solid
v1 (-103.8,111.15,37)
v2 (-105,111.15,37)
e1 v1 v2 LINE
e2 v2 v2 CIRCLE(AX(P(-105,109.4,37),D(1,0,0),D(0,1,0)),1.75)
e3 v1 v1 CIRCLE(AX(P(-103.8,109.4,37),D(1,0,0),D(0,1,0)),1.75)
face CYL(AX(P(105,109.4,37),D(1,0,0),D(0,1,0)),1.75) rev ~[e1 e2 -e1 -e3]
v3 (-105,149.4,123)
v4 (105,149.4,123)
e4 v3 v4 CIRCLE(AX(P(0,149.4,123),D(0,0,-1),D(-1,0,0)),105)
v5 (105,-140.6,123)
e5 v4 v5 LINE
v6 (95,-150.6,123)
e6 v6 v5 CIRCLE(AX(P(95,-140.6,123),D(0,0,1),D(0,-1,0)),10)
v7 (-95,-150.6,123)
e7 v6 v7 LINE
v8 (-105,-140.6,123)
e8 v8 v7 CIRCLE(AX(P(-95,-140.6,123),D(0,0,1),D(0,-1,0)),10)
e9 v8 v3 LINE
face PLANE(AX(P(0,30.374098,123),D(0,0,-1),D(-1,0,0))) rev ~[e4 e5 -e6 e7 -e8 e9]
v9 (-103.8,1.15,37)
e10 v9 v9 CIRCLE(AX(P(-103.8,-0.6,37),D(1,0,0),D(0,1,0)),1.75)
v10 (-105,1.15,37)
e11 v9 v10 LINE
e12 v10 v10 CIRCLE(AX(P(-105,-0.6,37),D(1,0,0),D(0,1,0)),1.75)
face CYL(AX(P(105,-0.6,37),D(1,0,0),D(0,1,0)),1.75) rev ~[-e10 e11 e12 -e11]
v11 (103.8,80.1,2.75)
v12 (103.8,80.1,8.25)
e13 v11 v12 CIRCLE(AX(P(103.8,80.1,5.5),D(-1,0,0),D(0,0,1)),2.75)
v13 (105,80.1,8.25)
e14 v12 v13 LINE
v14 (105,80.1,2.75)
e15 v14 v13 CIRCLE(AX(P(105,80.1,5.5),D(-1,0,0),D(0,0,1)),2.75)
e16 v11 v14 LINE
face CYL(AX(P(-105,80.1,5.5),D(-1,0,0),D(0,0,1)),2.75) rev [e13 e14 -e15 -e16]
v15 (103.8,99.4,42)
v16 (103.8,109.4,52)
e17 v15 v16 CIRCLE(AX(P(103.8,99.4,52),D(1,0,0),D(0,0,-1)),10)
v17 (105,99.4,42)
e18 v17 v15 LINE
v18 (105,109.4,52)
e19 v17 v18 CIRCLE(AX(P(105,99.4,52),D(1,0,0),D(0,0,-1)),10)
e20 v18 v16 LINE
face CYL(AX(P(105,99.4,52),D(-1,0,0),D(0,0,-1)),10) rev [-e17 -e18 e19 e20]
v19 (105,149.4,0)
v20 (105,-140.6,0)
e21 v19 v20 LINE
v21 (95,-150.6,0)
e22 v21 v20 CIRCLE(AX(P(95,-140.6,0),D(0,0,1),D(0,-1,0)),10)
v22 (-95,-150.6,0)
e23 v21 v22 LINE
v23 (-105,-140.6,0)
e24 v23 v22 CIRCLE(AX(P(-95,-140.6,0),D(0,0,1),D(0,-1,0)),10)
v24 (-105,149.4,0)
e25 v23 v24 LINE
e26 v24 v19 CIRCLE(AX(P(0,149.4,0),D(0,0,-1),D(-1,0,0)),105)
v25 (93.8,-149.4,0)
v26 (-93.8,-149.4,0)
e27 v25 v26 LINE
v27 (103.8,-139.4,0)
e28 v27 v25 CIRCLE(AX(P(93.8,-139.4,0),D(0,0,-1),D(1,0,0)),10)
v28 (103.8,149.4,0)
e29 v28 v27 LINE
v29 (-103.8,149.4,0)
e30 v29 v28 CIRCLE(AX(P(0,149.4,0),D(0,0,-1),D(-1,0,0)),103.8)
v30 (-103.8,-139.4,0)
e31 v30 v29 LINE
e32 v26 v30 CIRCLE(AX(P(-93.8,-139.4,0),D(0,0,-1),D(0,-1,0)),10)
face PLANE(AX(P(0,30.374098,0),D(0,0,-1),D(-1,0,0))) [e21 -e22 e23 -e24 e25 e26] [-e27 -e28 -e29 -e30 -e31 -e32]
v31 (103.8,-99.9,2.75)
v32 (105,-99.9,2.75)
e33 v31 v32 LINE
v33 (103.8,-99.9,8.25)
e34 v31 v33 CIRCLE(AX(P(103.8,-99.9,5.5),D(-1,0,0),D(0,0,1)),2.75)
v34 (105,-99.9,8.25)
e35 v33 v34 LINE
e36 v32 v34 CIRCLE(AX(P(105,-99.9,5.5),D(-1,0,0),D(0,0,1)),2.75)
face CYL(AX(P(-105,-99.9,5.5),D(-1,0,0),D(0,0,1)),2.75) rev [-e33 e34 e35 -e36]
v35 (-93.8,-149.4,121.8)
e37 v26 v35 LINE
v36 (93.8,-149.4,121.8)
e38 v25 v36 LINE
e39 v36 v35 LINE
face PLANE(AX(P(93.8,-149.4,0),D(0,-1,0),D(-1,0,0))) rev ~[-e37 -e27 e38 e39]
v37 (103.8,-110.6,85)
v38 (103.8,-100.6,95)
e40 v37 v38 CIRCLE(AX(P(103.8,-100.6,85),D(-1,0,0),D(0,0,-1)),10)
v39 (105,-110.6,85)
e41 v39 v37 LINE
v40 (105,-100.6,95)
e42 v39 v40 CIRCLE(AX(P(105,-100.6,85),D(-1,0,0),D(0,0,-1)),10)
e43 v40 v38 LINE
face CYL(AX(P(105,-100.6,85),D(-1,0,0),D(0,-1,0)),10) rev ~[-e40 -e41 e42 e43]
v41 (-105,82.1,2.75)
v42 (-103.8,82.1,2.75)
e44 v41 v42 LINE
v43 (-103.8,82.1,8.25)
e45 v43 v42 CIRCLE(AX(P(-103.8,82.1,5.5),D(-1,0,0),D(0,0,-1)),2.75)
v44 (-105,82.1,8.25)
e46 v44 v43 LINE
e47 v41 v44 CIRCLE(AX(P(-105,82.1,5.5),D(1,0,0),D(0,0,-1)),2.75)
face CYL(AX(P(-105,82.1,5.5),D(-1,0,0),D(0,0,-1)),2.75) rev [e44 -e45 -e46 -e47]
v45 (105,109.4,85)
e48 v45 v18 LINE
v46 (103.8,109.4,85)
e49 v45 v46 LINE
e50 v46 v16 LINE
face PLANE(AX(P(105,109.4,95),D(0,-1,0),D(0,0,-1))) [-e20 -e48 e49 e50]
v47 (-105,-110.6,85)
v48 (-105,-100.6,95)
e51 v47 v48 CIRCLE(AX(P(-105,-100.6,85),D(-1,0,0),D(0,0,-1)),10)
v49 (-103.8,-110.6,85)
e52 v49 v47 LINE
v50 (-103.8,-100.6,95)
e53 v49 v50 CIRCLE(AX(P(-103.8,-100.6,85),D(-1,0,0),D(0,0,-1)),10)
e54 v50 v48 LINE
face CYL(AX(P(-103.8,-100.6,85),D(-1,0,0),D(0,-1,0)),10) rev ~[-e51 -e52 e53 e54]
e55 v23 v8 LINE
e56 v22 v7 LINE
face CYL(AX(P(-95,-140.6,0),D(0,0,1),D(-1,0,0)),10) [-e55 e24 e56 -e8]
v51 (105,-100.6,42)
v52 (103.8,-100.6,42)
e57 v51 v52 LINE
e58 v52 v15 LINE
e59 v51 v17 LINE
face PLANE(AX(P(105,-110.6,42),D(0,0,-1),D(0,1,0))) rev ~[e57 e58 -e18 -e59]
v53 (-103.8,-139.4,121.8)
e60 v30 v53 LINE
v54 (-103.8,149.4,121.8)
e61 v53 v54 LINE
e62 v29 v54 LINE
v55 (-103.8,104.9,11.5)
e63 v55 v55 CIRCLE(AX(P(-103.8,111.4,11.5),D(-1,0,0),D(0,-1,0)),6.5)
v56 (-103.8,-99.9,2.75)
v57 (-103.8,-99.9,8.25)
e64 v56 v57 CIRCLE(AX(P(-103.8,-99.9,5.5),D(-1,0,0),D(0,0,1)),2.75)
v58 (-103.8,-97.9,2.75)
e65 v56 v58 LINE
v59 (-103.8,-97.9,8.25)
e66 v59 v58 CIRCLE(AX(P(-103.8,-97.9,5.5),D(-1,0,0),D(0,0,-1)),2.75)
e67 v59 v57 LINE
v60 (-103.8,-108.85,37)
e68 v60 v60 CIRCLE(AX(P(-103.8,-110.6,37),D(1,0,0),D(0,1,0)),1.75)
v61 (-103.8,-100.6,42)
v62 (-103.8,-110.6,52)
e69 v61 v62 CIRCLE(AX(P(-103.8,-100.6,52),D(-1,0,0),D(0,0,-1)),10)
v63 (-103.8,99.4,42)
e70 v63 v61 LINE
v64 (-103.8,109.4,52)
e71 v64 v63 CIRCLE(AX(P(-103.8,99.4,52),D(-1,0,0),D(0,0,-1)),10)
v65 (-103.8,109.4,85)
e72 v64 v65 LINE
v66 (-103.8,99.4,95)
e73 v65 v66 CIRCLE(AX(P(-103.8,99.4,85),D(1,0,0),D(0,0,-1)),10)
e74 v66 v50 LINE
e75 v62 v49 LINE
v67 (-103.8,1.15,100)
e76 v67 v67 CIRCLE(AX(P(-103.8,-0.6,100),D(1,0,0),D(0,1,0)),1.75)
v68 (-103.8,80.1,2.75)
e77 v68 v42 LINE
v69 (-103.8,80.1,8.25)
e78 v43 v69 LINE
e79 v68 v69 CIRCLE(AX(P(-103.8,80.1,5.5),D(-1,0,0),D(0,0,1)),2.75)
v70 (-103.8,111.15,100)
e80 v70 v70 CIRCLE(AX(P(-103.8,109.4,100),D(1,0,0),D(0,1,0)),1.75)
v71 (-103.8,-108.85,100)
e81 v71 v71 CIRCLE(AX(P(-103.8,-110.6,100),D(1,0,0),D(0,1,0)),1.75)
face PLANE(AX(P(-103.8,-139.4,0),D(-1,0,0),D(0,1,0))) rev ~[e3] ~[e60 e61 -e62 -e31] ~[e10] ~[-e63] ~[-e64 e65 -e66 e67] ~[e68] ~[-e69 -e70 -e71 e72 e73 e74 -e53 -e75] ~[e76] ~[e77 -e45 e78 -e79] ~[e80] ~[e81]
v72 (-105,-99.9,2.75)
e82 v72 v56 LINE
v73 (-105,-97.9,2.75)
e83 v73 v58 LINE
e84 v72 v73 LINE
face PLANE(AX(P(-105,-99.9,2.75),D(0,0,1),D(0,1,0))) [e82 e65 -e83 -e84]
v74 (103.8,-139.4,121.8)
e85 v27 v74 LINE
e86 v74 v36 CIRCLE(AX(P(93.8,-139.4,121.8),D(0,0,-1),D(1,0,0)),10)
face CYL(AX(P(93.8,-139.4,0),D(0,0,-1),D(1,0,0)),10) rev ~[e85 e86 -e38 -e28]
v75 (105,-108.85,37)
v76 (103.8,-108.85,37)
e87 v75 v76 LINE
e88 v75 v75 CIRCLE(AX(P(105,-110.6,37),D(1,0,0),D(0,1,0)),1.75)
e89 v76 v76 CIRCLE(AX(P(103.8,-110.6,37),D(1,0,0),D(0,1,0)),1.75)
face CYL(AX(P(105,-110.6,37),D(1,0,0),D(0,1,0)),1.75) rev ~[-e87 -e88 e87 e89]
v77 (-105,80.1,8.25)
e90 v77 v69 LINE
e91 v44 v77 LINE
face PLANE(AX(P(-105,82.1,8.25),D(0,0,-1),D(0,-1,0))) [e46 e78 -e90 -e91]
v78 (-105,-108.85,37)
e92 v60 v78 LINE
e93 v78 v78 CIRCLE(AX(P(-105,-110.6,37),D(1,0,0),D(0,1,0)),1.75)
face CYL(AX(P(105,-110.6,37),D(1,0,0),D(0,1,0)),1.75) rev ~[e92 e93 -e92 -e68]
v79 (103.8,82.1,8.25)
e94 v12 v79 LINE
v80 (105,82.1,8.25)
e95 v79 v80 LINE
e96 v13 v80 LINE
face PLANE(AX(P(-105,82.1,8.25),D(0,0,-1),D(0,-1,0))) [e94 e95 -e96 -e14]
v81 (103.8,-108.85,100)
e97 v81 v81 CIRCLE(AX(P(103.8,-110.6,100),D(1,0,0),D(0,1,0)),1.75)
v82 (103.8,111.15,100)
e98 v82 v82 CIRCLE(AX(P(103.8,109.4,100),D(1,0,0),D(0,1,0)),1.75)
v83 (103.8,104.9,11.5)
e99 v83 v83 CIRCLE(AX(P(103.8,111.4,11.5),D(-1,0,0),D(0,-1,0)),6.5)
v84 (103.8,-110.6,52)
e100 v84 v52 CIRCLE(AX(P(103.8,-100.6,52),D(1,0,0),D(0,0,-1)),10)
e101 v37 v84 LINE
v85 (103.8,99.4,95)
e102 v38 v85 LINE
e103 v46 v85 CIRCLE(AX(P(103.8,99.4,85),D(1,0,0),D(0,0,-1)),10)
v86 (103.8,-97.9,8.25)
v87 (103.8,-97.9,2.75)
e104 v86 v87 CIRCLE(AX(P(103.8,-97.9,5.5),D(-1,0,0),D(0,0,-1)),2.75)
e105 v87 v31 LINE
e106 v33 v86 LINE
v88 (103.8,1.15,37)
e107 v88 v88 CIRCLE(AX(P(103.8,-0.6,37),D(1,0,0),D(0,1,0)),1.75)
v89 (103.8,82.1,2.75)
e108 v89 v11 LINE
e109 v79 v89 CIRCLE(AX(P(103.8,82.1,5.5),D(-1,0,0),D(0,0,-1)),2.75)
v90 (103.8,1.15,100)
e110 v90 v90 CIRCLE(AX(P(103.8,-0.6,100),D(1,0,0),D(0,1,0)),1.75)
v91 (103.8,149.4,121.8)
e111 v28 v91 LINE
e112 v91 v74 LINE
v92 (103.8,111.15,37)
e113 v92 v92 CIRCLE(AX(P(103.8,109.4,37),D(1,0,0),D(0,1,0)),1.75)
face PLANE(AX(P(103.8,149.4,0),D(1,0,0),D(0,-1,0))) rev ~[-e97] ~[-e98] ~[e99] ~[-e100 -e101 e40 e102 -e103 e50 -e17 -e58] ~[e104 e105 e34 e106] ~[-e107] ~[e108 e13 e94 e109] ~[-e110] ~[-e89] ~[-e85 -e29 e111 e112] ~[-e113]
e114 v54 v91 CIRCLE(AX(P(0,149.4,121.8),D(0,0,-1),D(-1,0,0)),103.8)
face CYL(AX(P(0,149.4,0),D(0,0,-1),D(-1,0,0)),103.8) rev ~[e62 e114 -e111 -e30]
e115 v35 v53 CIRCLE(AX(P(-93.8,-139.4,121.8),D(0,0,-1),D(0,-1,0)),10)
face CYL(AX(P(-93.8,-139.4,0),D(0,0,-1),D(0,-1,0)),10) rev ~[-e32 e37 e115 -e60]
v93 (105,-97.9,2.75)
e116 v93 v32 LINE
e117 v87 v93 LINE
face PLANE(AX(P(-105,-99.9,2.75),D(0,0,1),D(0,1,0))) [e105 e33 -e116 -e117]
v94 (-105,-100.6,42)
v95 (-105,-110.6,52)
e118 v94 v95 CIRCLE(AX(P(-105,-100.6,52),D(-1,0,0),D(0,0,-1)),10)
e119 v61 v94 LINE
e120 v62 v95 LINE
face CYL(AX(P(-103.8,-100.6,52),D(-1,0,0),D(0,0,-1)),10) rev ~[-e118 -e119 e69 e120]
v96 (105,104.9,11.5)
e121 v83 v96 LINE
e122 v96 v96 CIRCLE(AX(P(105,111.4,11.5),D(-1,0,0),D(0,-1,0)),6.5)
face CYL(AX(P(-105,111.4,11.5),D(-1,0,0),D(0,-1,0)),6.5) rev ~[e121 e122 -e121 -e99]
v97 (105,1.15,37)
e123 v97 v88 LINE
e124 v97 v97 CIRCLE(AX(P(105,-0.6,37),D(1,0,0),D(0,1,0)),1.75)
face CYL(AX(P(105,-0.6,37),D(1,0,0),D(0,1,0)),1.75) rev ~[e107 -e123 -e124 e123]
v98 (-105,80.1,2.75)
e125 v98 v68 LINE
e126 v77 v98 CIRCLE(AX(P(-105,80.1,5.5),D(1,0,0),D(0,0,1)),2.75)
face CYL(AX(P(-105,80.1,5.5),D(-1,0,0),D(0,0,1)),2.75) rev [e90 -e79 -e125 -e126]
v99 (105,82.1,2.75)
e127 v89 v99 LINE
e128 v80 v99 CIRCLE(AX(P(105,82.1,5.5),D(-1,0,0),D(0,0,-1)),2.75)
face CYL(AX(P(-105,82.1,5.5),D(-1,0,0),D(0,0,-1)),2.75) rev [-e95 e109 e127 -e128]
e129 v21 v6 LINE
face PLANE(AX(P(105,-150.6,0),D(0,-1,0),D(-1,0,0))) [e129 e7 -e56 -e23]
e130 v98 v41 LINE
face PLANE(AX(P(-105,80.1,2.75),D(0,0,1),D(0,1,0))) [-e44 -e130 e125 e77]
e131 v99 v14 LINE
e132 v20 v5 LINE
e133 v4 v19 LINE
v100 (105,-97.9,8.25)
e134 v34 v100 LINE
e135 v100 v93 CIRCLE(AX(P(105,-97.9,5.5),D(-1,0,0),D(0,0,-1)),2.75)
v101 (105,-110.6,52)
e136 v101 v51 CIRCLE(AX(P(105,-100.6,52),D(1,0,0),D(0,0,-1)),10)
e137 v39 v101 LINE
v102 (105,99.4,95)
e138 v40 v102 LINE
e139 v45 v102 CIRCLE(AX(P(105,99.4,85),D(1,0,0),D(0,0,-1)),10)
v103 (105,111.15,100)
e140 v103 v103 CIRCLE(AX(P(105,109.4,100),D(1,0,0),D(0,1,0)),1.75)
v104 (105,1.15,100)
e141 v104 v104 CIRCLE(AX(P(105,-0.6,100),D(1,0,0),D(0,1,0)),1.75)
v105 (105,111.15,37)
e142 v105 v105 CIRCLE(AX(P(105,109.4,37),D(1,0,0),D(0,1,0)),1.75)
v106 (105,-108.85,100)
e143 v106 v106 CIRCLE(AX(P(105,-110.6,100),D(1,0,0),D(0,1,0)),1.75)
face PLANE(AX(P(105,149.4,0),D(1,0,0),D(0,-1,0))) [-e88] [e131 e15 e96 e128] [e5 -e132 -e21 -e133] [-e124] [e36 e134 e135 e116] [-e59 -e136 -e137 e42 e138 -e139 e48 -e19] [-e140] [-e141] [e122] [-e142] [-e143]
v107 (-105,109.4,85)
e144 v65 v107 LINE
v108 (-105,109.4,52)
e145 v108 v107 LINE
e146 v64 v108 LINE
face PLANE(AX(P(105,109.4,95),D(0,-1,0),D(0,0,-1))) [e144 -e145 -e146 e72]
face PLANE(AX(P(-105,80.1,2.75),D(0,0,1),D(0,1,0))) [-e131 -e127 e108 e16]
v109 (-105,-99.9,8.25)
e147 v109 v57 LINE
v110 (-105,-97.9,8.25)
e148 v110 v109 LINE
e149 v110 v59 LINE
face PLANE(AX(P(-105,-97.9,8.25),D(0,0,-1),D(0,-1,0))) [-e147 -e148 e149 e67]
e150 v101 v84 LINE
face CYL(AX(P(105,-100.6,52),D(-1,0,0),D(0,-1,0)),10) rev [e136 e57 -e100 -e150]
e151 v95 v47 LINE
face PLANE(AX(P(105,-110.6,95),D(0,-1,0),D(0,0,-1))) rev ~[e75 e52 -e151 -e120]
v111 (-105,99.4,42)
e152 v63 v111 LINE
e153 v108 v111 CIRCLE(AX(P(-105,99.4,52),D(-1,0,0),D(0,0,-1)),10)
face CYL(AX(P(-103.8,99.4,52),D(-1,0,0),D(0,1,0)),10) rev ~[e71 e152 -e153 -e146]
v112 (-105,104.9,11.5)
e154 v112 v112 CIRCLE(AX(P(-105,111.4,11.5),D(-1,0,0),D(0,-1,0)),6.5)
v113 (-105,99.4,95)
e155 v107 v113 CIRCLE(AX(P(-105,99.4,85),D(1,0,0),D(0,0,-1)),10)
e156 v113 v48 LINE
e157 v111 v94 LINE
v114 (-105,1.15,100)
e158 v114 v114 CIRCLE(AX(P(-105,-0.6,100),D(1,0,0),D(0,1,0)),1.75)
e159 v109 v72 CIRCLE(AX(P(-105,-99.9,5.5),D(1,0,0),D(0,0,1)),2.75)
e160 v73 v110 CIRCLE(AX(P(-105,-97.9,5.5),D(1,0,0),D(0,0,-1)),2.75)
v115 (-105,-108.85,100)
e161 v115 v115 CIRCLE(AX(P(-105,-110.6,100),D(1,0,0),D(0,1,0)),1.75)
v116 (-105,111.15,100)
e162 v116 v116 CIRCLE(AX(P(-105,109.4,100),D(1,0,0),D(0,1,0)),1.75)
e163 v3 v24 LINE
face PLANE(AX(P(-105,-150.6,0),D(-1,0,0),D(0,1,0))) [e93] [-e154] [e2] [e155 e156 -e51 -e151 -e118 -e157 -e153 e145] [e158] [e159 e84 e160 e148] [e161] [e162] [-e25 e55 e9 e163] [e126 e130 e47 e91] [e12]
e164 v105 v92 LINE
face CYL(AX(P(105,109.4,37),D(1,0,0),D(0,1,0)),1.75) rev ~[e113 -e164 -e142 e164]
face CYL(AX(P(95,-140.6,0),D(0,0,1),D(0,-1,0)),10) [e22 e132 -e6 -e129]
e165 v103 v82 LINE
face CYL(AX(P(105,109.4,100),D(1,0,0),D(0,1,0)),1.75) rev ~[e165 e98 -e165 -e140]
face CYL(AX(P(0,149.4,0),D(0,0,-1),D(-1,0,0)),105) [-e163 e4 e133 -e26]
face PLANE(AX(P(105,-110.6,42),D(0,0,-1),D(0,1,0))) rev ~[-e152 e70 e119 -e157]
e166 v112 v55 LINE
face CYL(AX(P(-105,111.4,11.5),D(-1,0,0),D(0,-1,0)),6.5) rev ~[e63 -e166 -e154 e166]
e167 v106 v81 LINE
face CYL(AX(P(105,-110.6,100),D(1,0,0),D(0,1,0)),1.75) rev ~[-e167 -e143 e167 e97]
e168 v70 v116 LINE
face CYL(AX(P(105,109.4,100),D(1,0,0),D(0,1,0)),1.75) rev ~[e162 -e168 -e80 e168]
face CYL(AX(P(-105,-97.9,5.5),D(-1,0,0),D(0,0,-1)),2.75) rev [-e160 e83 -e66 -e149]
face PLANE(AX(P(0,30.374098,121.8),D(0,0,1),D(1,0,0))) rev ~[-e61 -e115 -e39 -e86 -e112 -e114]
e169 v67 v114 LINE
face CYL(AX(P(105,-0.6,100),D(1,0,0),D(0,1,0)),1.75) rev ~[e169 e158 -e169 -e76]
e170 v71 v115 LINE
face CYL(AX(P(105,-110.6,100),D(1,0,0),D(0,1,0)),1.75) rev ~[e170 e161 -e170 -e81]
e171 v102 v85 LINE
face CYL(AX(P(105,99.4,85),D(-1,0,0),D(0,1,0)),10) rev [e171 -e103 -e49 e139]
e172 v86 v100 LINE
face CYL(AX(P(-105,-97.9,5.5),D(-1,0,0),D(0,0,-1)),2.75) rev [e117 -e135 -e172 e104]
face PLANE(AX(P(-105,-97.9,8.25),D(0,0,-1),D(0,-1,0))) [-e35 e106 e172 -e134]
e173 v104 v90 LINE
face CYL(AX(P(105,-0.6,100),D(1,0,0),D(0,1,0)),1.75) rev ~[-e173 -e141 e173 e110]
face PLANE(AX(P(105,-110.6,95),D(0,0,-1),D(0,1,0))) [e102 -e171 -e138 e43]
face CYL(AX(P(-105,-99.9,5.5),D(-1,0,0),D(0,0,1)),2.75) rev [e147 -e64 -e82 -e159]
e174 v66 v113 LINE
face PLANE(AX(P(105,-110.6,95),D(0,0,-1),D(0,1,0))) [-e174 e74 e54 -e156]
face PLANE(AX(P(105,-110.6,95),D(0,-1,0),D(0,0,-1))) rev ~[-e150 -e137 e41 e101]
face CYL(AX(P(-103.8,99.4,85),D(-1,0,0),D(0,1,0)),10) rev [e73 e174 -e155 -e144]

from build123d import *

# Parameters (mm, degrees)
BOSS_EXTRUDE1_DEPTH = 123
BOSS_EXTRUDE2_START = -1.2
BOSS_EXTRUDE2_DEPTH = 1.2
FILLET1_R           = 10
FILLET2_R           = 10
CUT_EXTRUDE1_DEPTH  = 353.063005725
SKETCH4_R           = 6.5
CUT_EXTRUDE2_DEPTH  = 353.063005725
SKETCH5_W           = 53
SKETCH5_H           = 220
CUT_EXTRUDE3_DEPTH  = 353.063005725
FILLET3_R           = 10
SKETCH6_R           = 1.75
CUT_EXTRUDE4_DEPTH  = 353.063005725


with BuildPart() as part:
    # Sketch1 → Boss-Extrude1 (new body)
    with BuildSketch(Plane.XY):
        with BuildLine():
            Line((-105, -150.6), (-105, 149.4))
            ThreePointArc((-105, 149.4), (0, 254.4), (105, 149.4))
            Line((105, 149.4), (105, -150.6))
            Line((105, -150.6), (-105, -150.6))
        make_face()
        with BuildLine():
            Line((93.8, -149.4), (-93.8, -149.4))
            ThreePointArc((-93.8, -149.4), (-100.871067812, -146.471067812), (-103.8, -139.4))
            Line((-103.8, -139.4), (-103.8, 149.4))
            ThreePointArc((-103.8, 149.4), (0, 253.2), (103.8, 149.4))
            Line((103.8, 149.4), (103.8, -139.4))
            ThreePointArc((103.8, -139.4), (100.871067812, -146.471067812), (93.8, -149.4))
        make_face(mode=Mode.SUBTRACT)
    extrude(amount=BOSS_EXTRUDE1_DEPTH)

    # Sketch2 → Boss-Extrude2 (add)
    with BuildSketch(Plane.XY.offset(123).offset(BOSS_EXTRUDE2_START)):
        with BuildLine():
            Line((-105, 149.4), (-105, -150.6))
            Line((-105, -150.6), (105, -150.6))
            Line((105, -150.6), (105, 149.4))
            ThreePointArc((105, 149.4), (0, 254.4), (-105, 149.4))
        make_face()
    extrude(amount=BOSS_EXTRUDE2_DEPTH)

    # Fillet1
    fillet1_edges = [part.edges().sort_by_distance(p)[0] for p in [
        (-105, -150.6, 61.5),
    ]]
    fillet(fillet1_edges, radius=FILLET1_R)

    # Fillet2
    fillet2_edges = [part.edges().sort_by_distance(p)[0] for p in [
        (105, -150.6, 61.5),
    ]]
    fillet(fillet2_edges, radius=FILLET2_R)

    # Sketch3 → Cut-Extrude1 (cut, through all)
    with BuildSketch(Plane.ZY.offset(105)):
        with BuildLine():
            Line((2.75, 80.1), (2.75, 82.1))
            ThreePointArc((2.75, 82.1), (5.5, 84.85), (8.25, 82.1))
            Line((8.25, 82.1), (8.25, 80.1))
            ThreePointArc((8.25, 80.1), (5.5, 77.35), (2.75, 80.1))
        make_face()
        with BuildLine():
            Line((2.75, -99.9), (2.75, -97.9))
            ThreePointArc((2.75, -97.9), (5.5, -95.15), (8.25, -97.9))
            Line((8.25, -97.9), (8.25, -99.9))
            ThreePointArc((8.25, -99.9), (5.5, -102.65), (2.75, -99.9))
        make_face()
    extrude(amount=-CUT_EXTRUDE1_DEPTH, mode=Mode.SUBTRACT)

    # Sketch4 → Cut-Extrude2 (cut, through all)
    with BuildSketch(Plane.ZY.offset(105)):
        with Locations(Location((11.5, 111.4, 0), (0, 0, 270))):
            Circle(SKETCH4_R)
    extrude(amount=-CUT_EXTRUDE2_DEPTH, mode=Mode.SUBTRACT)

    # Sketch5 → Cut-Extrude3 (cut, through all)
    with BuildSketch(Plane(origin=(105, 0, 0), x_dir=(0, 0, -1), z_dir=(1, 0, 0))):
        with Locations((-68.5, -0.6)):
            Rectangle(SKETCH5_W, SKETCH5_H)
    extrude(amount=-CUT_EXTRUDE3_DEPTH, mode=Mode.SUBTRACT)

    # Fillet3
    fillet3_edges = [part.edges().sort_by_distance(p)[0] for p in [
        (-104.4, 109.4, 95),
        (-104.4, 109.4, 42),
        (-104.4, -110.6, 42),
        (-104.4, -110.6, 95),
        (104.4, 109.4, 95),
        (104.4, 109.4, 42),
        (104.4, -110.6, 42),
        (104.4, -110.6, 95),
    ]]
    fillet(fillet3_edges, radius=FILLET3_R)

    # Sketch6 → Cut-Extrude4 (cut, through all)
    with BuildSketch(Plane(origin=(105, 0, 0), x_dir=(0, 0, -1), z_dir=(1, 0, 0))):
        with Locations(Location((-37, 109.4, 0), (0, 0, 90))):
            Circle(SKETCH6_R)
        with Locations(Location((-37, -0.6, 0), (0, 0, 90))):
            Circle(SKETCH6_R)
        with Locations(Location((-37, -110.6, 0), (0, 0, 90))):
            Circle(SKETCH6_R)
        with Locations(Location((-100, -110.6, 0), (0, 0, 90))):
            Circle(SKETCH6_R)
        with Locations(Location((-100, -0.6, 0), (0, 0, 90))):
            Circle(SKETCH6_R)
        with Locations(Location((-100, 109.4, 0), (0, 0, 90))):
            Circle(SKETCH6_R)
    extrude(amount=-CUT_EXTRUDE4_DEPTH, mode=Mode.SUBTRACT)


solid = part.part
